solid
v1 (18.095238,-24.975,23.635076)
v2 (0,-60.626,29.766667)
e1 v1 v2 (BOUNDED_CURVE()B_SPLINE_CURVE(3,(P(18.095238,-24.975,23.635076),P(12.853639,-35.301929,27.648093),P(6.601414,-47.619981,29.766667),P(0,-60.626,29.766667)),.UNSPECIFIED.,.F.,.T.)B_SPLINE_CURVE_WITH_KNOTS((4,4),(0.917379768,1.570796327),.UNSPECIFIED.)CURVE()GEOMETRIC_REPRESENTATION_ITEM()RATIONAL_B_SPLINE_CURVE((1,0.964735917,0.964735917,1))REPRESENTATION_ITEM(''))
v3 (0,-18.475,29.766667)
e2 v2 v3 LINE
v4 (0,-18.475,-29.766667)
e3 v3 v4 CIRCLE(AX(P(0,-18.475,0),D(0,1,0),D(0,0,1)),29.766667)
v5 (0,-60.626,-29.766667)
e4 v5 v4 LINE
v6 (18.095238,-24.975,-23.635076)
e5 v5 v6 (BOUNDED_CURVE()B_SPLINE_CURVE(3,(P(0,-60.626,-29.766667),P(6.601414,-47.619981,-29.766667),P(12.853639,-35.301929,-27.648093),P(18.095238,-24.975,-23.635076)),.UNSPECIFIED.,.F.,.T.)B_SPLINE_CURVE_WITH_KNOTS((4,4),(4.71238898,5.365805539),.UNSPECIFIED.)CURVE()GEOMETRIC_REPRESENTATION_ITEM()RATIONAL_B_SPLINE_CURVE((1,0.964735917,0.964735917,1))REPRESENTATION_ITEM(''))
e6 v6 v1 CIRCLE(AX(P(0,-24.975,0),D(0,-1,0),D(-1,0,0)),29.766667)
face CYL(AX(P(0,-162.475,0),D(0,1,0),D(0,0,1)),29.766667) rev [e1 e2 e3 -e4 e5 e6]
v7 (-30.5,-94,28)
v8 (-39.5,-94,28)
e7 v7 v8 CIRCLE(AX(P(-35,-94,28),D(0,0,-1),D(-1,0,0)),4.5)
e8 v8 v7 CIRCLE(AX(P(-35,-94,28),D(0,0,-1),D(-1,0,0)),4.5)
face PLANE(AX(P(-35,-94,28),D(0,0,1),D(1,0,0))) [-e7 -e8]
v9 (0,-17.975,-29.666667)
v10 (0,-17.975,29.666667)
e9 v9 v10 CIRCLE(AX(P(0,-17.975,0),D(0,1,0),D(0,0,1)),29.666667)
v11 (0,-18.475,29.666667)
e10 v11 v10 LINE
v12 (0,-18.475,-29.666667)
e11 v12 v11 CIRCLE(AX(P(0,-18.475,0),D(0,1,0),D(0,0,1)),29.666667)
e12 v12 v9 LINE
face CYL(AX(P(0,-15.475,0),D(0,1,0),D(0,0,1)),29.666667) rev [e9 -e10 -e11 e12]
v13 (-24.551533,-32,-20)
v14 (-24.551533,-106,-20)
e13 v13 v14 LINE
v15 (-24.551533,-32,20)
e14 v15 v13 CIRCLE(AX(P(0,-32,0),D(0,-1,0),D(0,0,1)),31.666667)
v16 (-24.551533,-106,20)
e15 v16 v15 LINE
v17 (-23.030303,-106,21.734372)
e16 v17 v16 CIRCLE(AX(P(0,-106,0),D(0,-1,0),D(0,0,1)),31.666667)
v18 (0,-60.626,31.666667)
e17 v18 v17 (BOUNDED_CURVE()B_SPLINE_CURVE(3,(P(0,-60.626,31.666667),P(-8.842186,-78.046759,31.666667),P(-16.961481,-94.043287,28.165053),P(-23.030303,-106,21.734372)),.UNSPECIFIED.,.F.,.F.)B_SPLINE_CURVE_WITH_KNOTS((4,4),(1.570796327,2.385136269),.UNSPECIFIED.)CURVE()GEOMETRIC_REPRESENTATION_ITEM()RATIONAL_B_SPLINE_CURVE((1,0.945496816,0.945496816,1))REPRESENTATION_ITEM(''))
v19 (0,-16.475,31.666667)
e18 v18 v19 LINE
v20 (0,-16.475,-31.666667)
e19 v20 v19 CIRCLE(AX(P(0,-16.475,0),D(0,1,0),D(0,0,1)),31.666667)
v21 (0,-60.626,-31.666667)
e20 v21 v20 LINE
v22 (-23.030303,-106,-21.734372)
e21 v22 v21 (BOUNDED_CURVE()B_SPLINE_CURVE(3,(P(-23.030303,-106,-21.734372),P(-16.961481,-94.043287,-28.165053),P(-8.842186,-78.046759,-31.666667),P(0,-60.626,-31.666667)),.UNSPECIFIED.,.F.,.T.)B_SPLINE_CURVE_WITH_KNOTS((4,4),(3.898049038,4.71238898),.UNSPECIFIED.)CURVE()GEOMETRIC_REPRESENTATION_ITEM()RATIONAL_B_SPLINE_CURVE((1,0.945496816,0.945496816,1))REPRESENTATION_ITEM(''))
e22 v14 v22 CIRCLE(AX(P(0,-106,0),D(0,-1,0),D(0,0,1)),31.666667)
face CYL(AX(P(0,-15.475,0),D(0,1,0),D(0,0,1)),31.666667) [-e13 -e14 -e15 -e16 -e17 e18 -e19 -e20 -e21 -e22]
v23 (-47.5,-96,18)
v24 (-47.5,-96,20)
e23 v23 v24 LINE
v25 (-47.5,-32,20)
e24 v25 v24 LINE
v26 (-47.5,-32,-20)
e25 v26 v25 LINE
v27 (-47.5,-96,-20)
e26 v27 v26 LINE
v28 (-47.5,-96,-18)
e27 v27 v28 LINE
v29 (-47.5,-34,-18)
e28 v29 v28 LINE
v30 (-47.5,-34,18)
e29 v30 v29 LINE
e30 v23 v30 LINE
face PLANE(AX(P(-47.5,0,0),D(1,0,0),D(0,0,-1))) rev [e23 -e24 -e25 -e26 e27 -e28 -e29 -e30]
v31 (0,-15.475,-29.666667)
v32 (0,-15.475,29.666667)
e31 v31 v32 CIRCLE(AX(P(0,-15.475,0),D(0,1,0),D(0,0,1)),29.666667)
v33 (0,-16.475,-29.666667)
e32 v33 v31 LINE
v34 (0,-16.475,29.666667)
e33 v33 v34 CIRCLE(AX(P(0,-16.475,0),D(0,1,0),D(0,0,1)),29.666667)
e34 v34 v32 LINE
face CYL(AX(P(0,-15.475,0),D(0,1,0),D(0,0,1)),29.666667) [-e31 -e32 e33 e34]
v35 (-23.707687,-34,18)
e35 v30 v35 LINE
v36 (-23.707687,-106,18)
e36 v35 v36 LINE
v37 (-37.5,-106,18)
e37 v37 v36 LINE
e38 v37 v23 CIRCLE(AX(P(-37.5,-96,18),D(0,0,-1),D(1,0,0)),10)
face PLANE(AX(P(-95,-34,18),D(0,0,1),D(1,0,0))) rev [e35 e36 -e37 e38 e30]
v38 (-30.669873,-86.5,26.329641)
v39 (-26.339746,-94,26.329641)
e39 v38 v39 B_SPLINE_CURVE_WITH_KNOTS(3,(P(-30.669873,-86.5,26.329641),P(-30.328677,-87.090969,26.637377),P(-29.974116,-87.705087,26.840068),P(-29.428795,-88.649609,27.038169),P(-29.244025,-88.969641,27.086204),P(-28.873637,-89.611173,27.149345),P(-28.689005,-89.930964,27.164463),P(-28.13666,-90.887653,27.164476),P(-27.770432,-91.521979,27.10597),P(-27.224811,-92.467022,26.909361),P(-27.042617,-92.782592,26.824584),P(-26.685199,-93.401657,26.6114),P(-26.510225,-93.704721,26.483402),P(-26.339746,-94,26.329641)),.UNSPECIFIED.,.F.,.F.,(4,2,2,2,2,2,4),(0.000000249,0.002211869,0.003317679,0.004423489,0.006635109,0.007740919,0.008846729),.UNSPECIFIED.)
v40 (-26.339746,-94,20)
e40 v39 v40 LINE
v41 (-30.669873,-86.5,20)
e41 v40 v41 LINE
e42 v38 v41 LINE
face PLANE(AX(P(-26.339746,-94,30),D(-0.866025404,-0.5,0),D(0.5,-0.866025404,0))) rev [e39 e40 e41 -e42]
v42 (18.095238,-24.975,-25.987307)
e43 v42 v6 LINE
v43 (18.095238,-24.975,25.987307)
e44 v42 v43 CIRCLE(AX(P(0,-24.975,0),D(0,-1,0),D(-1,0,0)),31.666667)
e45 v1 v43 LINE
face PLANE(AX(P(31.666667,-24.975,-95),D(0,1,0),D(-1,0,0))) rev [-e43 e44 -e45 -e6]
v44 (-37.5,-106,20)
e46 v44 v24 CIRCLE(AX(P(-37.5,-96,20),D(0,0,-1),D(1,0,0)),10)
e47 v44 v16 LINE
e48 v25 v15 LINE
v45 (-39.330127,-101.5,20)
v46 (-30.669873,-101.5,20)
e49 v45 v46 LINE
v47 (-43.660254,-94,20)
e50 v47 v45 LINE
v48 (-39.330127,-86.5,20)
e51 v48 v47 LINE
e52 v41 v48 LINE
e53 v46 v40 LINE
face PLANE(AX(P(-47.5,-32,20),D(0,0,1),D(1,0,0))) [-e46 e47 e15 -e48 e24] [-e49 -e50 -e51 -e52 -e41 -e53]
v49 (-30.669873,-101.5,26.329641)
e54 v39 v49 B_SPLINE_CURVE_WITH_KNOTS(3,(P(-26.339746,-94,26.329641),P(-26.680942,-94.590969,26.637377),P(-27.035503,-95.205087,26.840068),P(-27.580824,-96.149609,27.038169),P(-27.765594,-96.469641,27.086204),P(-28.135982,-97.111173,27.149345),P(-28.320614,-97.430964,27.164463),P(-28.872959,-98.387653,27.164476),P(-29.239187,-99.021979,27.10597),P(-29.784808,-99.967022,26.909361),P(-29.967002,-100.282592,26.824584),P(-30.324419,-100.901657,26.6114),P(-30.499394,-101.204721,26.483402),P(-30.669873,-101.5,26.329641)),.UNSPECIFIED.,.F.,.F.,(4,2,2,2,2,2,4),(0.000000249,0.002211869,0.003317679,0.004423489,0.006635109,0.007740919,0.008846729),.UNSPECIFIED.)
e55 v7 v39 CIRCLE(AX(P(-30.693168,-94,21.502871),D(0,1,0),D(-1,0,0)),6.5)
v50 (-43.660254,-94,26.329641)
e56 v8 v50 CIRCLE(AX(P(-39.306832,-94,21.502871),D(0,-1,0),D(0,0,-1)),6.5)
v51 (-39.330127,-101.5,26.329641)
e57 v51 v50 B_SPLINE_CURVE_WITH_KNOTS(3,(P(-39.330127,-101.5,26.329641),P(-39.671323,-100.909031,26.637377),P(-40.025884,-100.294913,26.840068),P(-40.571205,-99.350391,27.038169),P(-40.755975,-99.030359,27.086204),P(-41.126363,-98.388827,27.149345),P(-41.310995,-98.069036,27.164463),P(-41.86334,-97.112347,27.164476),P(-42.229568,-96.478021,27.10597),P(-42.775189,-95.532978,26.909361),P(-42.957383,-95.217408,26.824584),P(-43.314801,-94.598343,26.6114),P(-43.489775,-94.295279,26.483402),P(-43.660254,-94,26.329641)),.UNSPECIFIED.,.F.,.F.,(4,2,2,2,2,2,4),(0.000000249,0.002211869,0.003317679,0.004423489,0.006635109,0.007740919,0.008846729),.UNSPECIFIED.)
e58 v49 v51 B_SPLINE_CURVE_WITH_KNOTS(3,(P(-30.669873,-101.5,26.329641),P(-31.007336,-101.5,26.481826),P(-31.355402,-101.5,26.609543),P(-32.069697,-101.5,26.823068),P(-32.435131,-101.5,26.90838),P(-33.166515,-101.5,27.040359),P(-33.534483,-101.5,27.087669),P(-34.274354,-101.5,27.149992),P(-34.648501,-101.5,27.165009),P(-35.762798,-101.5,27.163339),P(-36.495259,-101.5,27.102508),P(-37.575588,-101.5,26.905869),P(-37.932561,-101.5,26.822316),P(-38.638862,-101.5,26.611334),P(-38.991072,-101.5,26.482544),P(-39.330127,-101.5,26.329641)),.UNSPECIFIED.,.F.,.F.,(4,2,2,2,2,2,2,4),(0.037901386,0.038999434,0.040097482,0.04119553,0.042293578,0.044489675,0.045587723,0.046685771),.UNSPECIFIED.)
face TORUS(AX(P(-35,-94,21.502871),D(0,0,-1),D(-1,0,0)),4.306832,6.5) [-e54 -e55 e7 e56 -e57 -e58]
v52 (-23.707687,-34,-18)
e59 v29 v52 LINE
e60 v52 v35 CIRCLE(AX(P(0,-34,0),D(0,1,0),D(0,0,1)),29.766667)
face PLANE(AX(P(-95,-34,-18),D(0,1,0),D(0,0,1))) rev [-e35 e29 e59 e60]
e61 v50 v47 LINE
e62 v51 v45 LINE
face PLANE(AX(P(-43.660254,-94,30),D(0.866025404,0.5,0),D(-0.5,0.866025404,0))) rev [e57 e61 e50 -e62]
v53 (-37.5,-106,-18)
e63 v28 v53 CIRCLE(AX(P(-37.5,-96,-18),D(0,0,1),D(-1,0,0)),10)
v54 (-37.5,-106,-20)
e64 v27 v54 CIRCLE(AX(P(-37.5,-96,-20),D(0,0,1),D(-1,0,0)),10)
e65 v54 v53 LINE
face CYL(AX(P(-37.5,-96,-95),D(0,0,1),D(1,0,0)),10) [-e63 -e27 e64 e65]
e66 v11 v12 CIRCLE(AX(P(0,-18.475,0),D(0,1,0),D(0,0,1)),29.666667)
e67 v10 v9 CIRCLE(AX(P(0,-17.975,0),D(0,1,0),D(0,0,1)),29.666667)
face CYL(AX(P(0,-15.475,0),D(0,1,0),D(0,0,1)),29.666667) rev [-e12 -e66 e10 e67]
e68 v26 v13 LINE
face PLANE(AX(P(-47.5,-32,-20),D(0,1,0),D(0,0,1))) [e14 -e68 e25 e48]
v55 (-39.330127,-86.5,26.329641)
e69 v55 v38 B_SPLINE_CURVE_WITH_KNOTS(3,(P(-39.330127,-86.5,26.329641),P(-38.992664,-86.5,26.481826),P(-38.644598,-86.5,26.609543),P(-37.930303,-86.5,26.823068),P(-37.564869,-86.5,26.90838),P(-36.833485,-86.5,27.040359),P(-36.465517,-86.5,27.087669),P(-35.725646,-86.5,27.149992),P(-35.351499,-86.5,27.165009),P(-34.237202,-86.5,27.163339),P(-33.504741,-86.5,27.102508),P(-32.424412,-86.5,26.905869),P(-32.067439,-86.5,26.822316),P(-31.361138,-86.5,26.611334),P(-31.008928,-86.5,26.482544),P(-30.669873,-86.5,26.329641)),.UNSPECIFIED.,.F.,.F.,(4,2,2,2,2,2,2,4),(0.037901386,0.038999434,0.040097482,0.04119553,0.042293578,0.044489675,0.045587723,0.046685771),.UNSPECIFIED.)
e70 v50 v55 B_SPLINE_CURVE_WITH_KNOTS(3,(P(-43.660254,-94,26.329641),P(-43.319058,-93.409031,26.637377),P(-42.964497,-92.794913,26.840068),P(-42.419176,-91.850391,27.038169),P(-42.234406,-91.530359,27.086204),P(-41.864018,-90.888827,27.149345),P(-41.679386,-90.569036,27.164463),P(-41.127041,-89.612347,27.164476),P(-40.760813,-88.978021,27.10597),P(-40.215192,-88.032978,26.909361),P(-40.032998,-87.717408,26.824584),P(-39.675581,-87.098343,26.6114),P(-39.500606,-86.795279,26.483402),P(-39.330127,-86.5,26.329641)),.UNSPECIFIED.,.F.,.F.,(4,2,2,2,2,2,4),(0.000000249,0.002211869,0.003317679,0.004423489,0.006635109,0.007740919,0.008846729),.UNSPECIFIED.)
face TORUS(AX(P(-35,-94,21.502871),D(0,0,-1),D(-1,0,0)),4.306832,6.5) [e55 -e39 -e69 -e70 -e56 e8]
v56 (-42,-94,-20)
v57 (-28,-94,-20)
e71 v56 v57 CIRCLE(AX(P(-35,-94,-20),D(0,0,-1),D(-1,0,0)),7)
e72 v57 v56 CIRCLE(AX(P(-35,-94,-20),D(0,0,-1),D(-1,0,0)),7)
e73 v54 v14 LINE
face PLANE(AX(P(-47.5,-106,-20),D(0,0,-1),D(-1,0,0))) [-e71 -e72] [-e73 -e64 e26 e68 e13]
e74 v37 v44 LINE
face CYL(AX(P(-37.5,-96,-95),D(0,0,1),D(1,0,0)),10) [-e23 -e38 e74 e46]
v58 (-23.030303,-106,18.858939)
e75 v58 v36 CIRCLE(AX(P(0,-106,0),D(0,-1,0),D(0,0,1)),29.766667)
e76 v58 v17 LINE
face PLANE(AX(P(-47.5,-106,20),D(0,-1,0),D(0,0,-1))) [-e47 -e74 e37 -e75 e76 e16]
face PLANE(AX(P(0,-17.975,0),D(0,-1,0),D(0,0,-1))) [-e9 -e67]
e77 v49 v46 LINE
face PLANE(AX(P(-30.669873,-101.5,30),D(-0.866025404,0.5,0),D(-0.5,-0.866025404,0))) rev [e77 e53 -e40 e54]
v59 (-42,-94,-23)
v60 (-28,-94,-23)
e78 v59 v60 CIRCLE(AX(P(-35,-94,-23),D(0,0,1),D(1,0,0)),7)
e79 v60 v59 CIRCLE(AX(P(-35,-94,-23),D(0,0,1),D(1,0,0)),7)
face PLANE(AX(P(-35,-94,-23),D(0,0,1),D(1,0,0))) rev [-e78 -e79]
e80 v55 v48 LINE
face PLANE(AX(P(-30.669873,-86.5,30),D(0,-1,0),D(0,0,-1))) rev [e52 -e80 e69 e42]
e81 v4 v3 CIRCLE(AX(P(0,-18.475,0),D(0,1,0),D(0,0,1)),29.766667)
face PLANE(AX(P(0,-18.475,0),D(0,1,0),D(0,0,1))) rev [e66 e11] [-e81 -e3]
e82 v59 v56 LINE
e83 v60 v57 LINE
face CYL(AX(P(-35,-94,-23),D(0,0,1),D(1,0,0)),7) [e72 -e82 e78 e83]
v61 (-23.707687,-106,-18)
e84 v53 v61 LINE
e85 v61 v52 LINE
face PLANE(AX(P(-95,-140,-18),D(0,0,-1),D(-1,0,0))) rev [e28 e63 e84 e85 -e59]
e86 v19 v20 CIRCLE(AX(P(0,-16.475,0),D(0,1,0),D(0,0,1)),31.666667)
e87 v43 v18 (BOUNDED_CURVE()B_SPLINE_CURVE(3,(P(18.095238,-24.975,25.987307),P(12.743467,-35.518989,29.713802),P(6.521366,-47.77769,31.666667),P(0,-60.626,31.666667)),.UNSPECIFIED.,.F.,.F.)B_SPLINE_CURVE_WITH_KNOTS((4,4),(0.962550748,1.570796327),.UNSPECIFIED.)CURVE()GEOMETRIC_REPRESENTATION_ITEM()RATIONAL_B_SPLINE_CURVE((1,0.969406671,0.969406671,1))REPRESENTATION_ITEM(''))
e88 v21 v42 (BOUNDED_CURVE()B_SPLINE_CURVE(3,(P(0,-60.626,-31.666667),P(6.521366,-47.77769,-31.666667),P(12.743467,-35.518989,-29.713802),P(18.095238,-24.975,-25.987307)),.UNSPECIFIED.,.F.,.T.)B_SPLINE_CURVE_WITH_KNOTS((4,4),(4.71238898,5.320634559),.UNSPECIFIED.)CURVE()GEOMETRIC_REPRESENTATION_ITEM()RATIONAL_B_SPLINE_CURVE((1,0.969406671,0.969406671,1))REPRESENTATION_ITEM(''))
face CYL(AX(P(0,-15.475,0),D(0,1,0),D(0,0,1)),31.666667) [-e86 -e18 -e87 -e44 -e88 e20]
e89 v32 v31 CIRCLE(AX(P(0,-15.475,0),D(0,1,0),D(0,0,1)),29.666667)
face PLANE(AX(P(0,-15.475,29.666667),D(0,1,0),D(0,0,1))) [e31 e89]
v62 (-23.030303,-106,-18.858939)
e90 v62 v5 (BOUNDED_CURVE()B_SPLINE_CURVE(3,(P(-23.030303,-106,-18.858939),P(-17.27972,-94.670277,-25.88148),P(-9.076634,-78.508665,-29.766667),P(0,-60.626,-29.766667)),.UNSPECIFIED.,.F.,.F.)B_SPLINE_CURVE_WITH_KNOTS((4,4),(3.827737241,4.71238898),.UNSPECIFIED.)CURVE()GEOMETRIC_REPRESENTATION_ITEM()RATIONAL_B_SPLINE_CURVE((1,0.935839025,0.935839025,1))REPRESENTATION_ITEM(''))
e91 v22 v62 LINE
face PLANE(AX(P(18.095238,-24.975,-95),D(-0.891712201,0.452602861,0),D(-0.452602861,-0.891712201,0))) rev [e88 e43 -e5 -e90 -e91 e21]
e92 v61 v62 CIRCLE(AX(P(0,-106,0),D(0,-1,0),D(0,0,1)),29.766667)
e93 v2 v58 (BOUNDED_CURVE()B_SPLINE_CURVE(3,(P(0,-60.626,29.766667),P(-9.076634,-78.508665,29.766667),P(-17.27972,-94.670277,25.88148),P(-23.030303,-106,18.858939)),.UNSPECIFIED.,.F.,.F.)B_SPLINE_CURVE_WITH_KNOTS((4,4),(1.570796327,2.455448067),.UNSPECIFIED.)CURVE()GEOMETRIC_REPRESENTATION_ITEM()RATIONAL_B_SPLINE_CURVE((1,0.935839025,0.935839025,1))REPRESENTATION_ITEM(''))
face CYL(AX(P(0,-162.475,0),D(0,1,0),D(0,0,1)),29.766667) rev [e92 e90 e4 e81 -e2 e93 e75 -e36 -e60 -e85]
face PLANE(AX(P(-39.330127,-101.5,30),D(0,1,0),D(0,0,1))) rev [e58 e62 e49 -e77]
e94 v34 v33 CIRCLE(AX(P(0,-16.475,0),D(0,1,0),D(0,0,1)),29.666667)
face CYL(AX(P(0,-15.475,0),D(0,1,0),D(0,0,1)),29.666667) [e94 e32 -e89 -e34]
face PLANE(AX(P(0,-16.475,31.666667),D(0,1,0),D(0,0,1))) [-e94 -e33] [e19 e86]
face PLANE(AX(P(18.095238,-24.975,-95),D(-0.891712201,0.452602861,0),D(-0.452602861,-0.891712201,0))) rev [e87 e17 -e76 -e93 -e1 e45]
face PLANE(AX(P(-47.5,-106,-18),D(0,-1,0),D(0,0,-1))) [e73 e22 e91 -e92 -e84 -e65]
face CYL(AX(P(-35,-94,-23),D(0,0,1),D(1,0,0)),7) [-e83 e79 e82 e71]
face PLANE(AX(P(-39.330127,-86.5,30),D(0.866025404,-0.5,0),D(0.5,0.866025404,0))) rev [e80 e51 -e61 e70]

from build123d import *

# Parameters (mm, degrees)
SKETCH2_W               = 36
SKETCH2_H               = 106
CUT_EXTRUDE1_DEPTH      = 95
BOSS_EXTRUDE1_DEPTH     = 47.5
SKETCH4_R               = 29.766666667
CUT_EXTRUDE2_DEPTH      = 144
CUT_EXTRUDE3_DEPTH      = 95
CUT_EXTRUDE3_DEPTH_BACK = 95
SKETCH6_R               = 7
BOSS_EXTRUDE2_DEPTH     = 3
SKETCH8_R               = 9
CUT_EXTRUDE4_DEPTH      = 10


with BuildPart() as part:
    # Sketch1 → Revolve1 (revolve)
    with BuildSketch(Plane(origin=(0, 0, 0), x_dir=(0, 0, -1), z_dir=(1, 0, 0))):
        Polygon((0, -17.975), (-29.666666667, -17.975), (-29.666666667, -109.475), (-31.666666667, -109.475), (-31.666666667, -16.475), (-29.666666667, -16.475), (-29.666666667, -15.475), (0, -15.475), align=None)
    revolve(axis=Axis((0, -15.475, 0), (0, -1, 0)))

    # Sketch2 → Cut-Extrude1 (cut)
    with BuildSketch(Plane(origin=(0, 0, 0), x_dir=(0, 0, -1), z_dir=(1, 0, 0))):
        with Locations((0, -87)):
            Rectangle(SKETCH2_W, SKETCH2_H)
    extrude(amount=-CUT_EXTRUDE1_DEPTH, mode=Mode.SUBTRACT)

    # Sketch3 → Boss-Extrude1 (add)
    with BuildSketch(Plane(origin=(0, 0, 0), x_dir=(0, 0, -1), z_dir=(1, 0, 0))):
        Polygon((-20, -32), (-20, -106), (-18, -106), (-18, -34), (18, -34), (18, -106), (20, -106), (20, -32), align=None)
    extrude(amount=-BOSS_EXTRUDE1_DEPTH)

    # Sketch4 → Cut-Extrude2 (cut)
    with BuildSketch(Plane(origin=(0, -18.475, 0), x_dir=(1, 0, 0), z_dir=(0, 1, 0))):
        with Locations(Location((0, 0, 0), (0, 0, 270))):
            Circle(SKETCH4_R)
    extrude(amount=-CUT_EXTRUDE2_DEPTH, mode=Mode.SUBTRACT)

    # Sketch5 → Cut-Extrude3 (cut, two sides: drawn at the far end of the back side and taken through both)
    with BuildSketch(Plane.XY.offset(-CUT_EXTRUDE3_DEPTH_BACK)):
        with BuildLine():
            Line((-81.666666667, -159.475), (31.666666667, -159.475))
            Line((31.666666667, -159.475), (31.666666667, -24.975))
            Line((31.666666667, -24.975), (18.095238095, -24.975))
            Line((18.095238095, -24.975), (-23.03030303, -106))
            Line((-23.03030303, -106), (-37.5, -106))
            ThreePointArc((-37.5, -106), (-44.571067812, -103.071067812), (-47.5, -96))
            Line((-47.5, -96), (-47.5, -61.653061224))
            Line((-47.5, -61.653061224), (-81.666666667, -106))
            Line((-81.666666667, -106), (-81.666666667, -159.475))
        make_face()
    extrude(amount=CUT_EXTRUDE3_DEPTH + CUT_EXTRUDE3_DEPTH_BACK, mode=Mode.SUBTRACT)

    # Sketch6 → Boss-Extrude2 (add)
    with BuildSketch(Plane.XY.offset(-20)):
        with Locations((-35, -94)):
            Circle(SKETCH6_R)
    extrude(amount=-BOSS_EXTRUDE2_DEPTH)

    # Sketch7 → Revolve2 (revolve)
    with BuildSketch(Plane(origin=(-35, 0, 0), x_dir=(0, 0, -1), z_dir=(1, 0, 0)), mode=Mode.PRIVATE) as revolve2_sk:
        with BuildLine():
            Line((-28, -94), (-28, -89.5))
            ThreePointArc((-28, -89.5), (-27.442646012, -87.053268439), (-26, -85))
            Line((-26, -85), (-20, -85))
            Line((-20, -85), (-20, -94))
            Line((-20, -94), (-28, -94))
        make_face()
    revolve(revolve2_sk.sketch.rotate(Axis((-35, -94, 20), (0, 0, 1)), 90), axis=Axis((-35, -94, 20), (0, 0, 1)))

    # Sketch8 → Cut-Extrude4 (cut)
    with BuildSketch(Plane.XY.offset(20)):
        with Locations((-35, -94)):
            Circle(SKETCH8_R)
        Polygon((-43.660254038, -94), (-39.330127019, -101.5), (-30.669872981, -101.5), (-26.339745962, -94), (-30.669872981, -86.5), (-39.330127019, -86.5), align=None, mode=Mode.SUBTRACT)
    extrude(amount=CUT_EXTRUDE4_DEPTH, mode=Mode.SUBTRACT)


solid = part.part
